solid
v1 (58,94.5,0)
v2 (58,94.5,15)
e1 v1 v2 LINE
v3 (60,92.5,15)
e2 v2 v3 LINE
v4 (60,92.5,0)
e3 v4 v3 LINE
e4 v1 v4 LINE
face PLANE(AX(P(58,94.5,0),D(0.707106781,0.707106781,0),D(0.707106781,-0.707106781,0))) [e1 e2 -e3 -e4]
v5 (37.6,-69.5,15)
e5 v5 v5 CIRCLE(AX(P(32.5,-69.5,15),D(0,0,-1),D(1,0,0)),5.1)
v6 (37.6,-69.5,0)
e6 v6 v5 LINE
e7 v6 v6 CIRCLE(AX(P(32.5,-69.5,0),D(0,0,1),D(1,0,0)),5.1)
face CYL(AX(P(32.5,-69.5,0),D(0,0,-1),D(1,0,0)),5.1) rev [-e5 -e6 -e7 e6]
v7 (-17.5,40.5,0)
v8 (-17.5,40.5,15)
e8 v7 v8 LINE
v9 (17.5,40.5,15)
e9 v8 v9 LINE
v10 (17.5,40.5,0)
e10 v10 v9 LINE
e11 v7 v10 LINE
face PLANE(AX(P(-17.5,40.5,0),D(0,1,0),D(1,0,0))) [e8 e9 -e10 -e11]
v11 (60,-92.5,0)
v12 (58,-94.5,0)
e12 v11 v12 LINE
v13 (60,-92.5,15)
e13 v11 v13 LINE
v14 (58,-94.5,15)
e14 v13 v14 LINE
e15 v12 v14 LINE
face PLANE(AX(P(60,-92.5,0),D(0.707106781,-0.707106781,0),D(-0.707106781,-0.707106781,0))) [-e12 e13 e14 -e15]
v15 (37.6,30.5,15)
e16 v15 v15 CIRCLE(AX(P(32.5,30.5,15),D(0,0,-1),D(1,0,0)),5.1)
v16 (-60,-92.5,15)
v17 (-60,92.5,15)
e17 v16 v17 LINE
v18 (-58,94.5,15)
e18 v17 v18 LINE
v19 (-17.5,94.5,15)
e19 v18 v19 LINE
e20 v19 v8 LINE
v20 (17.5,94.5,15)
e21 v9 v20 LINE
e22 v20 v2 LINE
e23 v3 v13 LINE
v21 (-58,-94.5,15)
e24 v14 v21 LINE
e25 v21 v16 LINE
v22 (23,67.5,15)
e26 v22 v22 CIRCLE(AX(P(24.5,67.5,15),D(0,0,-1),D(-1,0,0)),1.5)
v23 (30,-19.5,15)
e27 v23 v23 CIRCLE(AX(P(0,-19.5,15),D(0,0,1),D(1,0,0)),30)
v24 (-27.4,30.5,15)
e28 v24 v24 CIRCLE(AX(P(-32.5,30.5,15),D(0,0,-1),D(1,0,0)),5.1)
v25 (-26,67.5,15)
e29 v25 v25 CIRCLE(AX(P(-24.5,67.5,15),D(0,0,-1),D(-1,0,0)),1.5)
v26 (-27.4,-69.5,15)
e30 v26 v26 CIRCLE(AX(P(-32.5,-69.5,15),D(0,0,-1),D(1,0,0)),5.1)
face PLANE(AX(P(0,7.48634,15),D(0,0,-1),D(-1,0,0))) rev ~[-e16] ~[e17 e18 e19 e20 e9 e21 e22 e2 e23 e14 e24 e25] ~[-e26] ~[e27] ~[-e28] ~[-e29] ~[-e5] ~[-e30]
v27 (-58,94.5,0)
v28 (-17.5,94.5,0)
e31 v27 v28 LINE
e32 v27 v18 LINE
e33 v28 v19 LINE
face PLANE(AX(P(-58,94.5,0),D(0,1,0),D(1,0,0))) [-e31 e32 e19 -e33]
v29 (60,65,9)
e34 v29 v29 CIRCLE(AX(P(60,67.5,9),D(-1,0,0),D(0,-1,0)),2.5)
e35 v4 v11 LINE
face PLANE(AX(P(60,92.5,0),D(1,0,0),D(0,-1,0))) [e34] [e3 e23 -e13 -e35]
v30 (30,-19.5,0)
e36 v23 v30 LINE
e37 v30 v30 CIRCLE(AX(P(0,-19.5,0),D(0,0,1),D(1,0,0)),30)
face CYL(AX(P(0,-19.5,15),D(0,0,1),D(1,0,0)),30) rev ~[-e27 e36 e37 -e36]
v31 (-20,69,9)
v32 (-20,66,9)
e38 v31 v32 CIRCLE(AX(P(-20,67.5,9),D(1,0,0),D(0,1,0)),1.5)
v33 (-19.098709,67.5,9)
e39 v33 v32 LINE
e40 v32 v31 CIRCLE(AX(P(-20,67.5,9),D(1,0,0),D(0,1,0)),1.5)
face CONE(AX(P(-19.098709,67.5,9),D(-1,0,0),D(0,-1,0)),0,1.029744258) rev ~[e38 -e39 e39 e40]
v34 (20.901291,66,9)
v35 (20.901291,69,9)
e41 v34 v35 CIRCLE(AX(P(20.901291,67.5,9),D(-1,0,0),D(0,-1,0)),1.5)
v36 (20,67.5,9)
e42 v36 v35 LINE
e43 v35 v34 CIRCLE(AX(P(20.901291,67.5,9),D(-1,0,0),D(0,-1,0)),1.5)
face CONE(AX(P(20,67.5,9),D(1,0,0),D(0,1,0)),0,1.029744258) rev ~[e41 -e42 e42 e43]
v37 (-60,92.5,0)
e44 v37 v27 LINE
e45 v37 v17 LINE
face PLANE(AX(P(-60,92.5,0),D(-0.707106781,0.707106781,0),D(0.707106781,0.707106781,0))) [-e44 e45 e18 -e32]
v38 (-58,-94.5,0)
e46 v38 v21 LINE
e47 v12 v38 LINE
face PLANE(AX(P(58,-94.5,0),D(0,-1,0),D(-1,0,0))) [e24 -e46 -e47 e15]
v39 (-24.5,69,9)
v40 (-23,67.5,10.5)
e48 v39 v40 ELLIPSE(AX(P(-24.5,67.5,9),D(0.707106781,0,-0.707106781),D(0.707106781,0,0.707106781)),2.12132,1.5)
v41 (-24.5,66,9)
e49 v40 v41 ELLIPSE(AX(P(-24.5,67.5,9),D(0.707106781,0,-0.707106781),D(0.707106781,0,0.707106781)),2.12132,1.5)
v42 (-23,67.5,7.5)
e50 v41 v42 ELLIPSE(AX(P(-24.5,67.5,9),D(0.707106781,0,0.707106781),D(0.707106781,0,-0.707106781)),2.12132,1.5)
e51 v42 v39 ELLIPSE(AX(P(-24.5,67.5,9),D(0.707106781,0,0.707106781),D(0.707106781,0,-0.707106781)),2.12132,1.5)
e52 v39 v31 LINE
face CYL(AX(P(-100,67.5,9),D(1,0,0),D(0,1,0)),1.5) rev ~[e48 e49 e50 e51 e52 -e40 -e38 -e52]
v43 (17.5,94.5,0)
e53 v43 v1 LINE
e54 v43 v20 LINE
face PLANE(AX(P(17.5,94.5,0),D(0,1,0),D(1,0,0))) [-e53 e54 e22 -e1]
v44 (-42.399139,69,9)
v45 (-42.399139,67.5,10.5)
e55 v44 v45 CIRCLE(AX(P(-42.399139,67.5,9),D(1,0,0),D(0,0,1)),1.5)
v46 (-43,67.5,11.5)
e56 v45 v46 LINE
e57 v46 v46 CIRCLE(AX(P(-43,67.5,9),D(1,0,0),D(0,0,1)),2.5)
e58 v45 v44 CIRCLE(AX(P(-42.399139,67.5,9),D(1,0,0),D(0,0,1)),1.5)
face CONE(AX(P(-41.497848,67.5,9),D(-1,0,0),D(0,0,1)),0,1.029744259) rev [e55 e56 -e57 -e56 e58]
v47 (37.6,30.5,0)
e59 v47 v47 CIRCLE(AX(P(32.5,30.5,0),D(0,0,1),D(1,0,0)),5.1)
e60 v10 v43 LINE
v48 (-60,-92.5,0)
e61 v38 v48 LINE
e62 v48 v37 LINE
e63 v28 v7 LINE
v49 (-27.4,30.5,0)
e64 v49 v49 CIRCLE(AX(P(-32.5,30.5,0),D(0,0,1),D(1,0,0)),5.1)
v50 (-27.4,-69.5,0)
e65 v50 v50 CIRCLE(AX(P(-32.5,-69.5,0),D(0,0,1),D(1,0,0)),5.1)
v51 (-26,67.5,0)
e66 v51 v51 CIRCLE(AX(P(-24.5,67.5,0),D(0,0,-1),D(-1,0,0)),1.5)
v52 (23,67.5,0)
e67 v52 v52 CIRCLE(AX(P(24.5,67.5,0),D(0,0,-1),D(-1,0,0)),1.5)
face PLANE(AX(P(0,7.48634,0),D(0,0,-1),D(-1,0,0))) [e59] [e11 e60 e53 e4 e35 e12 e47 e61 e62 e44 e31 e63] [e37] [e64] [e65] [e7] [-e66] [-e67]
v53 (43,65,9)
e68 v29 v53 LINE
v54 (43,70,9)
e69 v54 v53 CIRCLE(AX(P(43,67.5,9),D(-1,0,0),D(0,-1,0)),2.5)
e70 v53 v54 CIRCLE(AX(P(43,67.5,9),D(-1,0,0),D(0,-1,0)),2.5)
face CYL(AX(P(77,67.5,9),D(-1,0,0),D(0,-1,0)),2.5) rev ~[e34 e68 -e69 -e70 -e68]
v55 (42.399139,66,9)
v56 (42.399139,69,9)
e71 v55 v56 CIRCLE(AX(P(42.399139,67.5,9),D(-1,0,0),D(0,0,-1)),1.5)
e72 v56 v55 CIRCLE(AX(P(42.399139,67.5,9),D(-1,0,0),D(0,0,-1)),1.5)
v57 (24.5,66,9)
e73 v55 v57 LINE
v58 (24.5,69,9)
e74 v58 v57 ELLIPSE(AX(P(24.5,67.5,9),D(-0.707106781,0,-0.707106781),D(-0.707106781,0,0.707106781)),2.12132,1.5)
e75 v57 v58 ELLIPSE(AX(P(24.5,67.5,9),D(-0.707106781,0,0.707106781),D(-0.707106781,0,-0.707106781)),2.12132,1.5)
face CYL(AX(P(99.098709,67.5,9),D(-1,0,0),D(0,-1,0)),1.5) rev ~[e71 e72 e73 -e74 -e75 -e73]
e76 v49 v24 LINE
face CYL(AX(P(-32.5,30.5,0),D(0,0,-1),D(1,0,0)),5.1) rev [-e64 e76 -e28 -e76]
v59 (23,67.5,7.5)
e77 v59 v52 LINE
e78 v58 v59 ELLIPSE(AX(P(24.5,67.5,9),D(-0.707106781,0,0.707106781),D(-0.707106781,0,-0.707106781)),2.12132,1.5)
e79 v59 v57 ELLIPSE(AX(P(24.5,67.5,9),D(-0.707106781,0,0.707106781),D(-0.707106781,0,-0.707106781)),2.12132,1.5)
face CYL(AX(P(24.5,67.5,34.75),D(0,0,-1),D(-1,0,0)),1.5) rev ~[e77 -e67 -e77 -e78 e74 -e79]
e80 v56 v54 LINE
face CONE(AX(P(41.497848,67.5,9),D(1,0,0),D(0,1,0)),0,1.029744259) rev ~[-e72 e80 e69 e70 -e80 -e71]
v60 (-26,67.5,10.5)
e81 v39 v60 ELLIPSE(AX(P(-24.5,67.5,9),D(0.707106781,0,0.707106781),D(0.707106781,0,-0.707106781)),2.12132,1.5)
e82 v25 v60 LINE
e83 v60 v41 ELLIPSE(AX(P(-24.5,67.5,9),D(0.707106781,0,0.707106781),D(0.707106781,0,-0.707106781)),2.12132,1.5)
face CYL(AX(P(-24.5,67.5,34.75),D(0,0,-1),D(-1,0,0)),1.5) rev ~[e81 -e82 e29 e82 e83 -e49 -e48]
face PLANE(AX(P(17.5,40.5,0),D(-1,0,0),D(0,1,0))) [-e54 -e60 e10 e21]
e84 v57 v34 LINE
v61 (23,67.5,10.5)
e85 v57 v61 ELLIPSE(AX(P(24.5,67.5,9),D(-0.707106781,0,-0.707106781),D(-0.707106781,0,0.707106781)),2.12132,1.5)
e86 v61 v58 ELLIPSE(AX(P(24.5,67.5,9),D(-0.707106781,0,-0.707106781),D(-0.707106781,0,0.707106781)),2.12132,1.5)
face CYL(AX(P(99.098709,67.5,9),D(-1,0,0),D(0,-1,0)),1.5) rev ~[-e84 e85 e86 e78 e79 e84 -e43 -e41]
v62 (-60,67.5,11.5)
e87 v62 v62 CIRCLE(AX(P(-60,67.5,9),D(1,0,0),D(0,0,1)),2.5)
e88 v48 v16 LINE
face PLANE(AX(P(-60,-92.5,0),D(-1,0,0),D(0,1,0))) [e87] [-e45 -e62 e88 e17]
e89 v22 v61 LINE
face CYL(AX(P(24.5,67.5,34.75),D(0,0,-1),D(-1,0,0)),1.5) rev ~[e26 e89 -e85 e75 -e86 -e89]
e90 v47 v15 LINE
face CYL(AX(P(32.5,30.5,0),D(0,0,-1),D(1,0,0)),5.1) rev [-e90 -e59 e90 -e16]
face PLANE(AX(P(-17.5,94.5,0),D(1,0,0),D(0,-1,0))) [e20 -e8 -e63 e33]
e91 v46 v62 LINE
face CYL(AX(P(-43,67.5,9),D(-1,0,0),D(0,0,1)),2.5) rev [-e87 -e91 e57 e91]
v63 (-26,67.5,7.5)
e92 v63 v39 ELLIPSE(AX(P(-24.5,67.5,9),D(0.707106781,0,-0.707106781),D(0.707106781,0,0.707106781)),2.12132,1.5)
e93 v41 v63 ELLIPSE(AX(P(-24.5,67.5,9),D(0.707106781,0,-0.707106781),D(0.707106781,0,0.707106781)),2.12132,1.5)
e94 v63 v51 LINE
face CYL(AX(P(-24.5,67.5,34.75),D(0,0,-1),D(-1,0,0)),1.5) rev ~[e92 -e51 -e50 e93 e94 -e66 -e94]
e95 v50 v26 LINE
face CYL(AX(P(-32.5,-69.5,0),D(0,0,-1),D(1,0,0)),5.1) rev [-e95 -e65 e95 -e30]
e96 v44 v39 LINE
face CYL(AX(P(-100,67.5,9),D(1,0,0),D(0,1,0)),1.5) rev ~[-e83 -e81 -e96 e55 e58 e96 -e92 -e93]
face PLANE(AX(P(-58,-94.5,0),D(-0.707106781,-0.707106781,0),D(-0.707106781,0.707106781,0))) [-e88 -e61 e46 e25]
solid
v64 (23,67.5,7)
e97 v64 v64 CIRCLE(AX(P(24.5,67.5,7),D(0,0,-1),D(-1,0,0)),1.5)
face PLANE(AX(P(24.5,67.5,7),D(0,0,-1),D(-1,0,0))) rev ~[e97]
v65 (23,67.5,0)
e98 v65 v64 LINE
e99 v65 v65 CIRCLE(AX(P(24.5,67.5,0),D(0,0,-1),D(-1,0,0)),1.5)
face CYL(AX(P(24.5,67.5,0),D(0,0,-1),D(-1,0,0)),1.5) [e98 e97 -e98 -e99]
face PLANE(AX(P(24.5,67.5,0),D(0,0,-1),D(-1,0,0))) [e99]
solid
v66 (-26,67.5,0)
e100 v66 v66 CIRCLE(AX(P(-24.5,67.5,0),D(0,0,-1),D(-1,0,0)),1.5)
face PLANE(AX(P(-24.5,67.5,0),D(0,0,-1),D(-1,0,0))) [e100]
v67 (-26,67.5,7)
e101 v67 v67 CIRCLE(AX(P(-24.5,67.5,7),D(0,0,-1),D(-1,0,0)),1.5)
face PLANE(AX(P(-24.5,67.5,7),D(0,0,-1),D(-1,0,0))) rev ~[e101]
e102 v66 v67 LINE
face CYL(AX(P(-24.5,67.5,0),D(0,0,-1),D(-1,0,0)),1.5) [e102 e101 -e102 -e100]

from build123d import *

# Parameters (mm, degrees)
SKETCH1_R                  = 5.1
BOSS_EXTRUDE1_DEPTH        = 15
SIZE_MM_DOWEL_HOLE_1_D     = 3
SIZE_MM_DOWEL_HOLE_1_DEPTH = 39.098709071
SIZE_MM_DOWEL_HOLE_1_TIP   = 0.901290929
SIZE_MM_DOWEL_HOLE_2_D     = 3
SIZE_MM_DOWEL_HOLE_2_DEPTH = 40
SIZE_MM_DOWEL_HOLE_2_TIP   = 0.901290929
M6_TAPPED_HOLE2_D          = 5
M6_TAPPED_HOLE2_DEPTH      = 17
M6_TAPPED_HOLE2_TIP        = 1.502151548
M12_TAPPED_HOLE1_D         = 10.2
SKETCH26_R                 = 30
CUT_EXTRUDE8_DEPTH         = 20
SIZE_MM_DOWEL_HOLE_3_D     = 3
SIZE_MM_DOWEL_HOLE_3_DEPTH = 19.75
SIZE_MM_DOWEL_HOLE_3_TIP   = 0.901290929
SKETCH28_R                 = 1.5
BOSS_EXTRUDE2_DEPTH        = 7
BOSS_EXTRUDE2_2_DEPTH      = 7


with BuildPart() as part:
    # Sketch1 → Boss-Extrude1 (new body)
    with BuildSketch(Plane.XY):
        Polygon((17.5, 94.5), (58, 94.5), (60, 92.5), (60, -92.5), (58, -94.5), (-58, -94.5), (-60, -92.5), (-60, 92.5), (-58, 94.5), (-17.5, 94.5), (-17.5, 40.5), (17.5, 40.5), align=None)
        with Locations((-32.5, -69.5)):
            Circle(SKETCH1_R, mode=Mode.SUBTRACT)
        with Locations((-32.5, 30.5)):
            Circle(SKETCH1_R, mode=Mode.SUBTRACT)
        with Locations((32.5, 30.5)):
            Circle(SKETCH1_R, mode=Mode.SUBTRACT)
        with Locations((32.5, -69.5)):
            Circle(SKETCH1_R, mode=Mode.SUBTRACT)
    extrude(amount=BOSS_EXTRUDE1_DEPTH)

    # Size mm dowel hole 1
    with Locations(Plane(origin=(60, 67.5, 9), x_dir=(0, 1, 0), z_dir=(1, 0, 0))):
        with Locations((0, 0)):
            Hole(SIZE_MM_DOWEL_HOLE_1_D / 2, depth=SIZE_MM_DOWEL_HOLE_1_DEPTH)
            with Locations((0, 0, -(SIZE_MM_DOWEL_HOLE_1_DEPTH + SIZE_MM_DOWEL_HOLE_1_TIP / 2))):  # 118° drill point
                Cone(0, SIZE_MM_DOWEL_HOLE_1_D / 2, SIZE_MM_DOWEL_HOLE_1_TIP, mode=Mode.SUBTRACT)

    # Size mm dowel hole 2
    with Locations(Plane(origin=(-60, 67.5, 9), x_dir=(0, -1, 0), z_dir=(-1, 0, 0))):
        with Locations((0, 0)):
            Hole(SIZE_MM_DOWEL_HOLE_2_D / 2, depth=SIZE_MM_DOWEL_HOLE_2_DEPTH)
            with Locations((0, 0, -(SIZE_MM_DOWEL_HOLE_2_DEPTH + SIZE_MM_DOWEL_HOLE_2_TIP / 2))):  # 118° drill point
                Cone(0, SIZE_MM_DOWEL_HOLE_2_D / 2, SIZE_MM_DOWEL_HOLE_2_TIP, mode=Mode.SUBTRACT)

    # Sketch22 → M6 Tapped Hole1 (revolve, cut)
    with BuildSketch(Plane(origin=(-60, 67.5, 9), x_dir=(0, 0, 1), z_dir=(0, 1, 0))):
        Polygon((0, 0), (0, 18.502151548), (2.5, 17), (2.5, 0), align=None)
    revolve(axis=Axis((-66.35, 67.5, 9), (1, 0, 0)), mode=Mode.SUBTRACT)

    # M6 Tapped Hole2
    with Locations(Plane(origin=(60, 67.5, 9), x_dir=(0, 1, 0), z_dir=(1, 0, 0))):
        with Locations((0, 0)):
            Hole(M6_TAPPED_HOLE2_D / 2, depth=M6_TAPPED_HOLE2_DEPTH)
            with Locations((0, 0, -(M6_TAPPED_HOLE2_DEPTH + M6_TAPPED_HOLE2_TIP / 2))):  # 118° drill point
                Cone(0, M6_TAPPED_HOLE2_D / 2, M6_TAPPED_HOLE2_TIP, mode=Mode.SUBTRACT)

    # M12 Tapped Hole1 (through all)
    with Locations(Plane(origin=(-32.5, 30.5, 15), x_dir=(1, 0, 0), z_dir=(0, 0, 1))):
        with Locations((0, 0), (65, 0), (65, -100), (0, -100)):
            Hole(M12_TAPPED_HOLE1_D / 2)

    # Sketch26 → Cut-Extrude8 (cut)
    with BuildSketch(Plane.XY.offset(15)):
        with Locations((0, -19.5)):
            Circle(SKETCH26_R)
    extrude(amount=-CUT_EXTRUDE8_DEPTH, mode=Mode.SUBTRACT)

    # Size mm dowel hole 3
    with Locations(Plane(origin=(-24.5, 67.5, 15), x_dir=(1, 0, 0), z_dir=(0, 0, 1))):
        with Locations((0, 0), (49, 0)):
            Hole(SIZE_MM_DOWEL_HOLE_3_D / 2, depth=SIZE_MM_DOWEL_HOLE_3_DEPTH)
            with Locations((0, 0, -(SIZE_MM_DOWEL_HOLE_3_DEPTH + SIZE_MM_DOWEL_HOLE_3_TIP / 2))):  # 118° drill point
                Cone(0, SIZE_MM_DOWEL_HOLE_3_D / 2, SIZE_MM_DOWEL_HOLE_3_TIP, mode=Mode.SUBTRACT)


with BuildPart() as body_2:
    # Sketch28 → Boss-Extrude2 (new body)
    with BuildSketch(Plane(origin=(0, 0, 0), x_dir=(-1, 0, 0), z_dir=(0, 0, -1))):
        with Locations((24.5, 67.5)):
            Circle(SKETCH28_R)
    extrude(amount=-BOSS_EXTRUDE2_DEPTH)


with BuildPart() as body_3:
    # Sketch28 → Boss-Extrude2 2 (new body)
    with BuildSketch(Plane(origin=(0, 0, 0), x_dir=(-1, 0, 0), z_dir=(0, 0, -1))):
        with Locations((-24.5, 67.5)):
            Circle(SKETCH28_R)
    extrude(amount=-BOSS_EXTRUDE2_2_DEPTH)


solid = Compound([part.part, body_2.part, body_3.part])
